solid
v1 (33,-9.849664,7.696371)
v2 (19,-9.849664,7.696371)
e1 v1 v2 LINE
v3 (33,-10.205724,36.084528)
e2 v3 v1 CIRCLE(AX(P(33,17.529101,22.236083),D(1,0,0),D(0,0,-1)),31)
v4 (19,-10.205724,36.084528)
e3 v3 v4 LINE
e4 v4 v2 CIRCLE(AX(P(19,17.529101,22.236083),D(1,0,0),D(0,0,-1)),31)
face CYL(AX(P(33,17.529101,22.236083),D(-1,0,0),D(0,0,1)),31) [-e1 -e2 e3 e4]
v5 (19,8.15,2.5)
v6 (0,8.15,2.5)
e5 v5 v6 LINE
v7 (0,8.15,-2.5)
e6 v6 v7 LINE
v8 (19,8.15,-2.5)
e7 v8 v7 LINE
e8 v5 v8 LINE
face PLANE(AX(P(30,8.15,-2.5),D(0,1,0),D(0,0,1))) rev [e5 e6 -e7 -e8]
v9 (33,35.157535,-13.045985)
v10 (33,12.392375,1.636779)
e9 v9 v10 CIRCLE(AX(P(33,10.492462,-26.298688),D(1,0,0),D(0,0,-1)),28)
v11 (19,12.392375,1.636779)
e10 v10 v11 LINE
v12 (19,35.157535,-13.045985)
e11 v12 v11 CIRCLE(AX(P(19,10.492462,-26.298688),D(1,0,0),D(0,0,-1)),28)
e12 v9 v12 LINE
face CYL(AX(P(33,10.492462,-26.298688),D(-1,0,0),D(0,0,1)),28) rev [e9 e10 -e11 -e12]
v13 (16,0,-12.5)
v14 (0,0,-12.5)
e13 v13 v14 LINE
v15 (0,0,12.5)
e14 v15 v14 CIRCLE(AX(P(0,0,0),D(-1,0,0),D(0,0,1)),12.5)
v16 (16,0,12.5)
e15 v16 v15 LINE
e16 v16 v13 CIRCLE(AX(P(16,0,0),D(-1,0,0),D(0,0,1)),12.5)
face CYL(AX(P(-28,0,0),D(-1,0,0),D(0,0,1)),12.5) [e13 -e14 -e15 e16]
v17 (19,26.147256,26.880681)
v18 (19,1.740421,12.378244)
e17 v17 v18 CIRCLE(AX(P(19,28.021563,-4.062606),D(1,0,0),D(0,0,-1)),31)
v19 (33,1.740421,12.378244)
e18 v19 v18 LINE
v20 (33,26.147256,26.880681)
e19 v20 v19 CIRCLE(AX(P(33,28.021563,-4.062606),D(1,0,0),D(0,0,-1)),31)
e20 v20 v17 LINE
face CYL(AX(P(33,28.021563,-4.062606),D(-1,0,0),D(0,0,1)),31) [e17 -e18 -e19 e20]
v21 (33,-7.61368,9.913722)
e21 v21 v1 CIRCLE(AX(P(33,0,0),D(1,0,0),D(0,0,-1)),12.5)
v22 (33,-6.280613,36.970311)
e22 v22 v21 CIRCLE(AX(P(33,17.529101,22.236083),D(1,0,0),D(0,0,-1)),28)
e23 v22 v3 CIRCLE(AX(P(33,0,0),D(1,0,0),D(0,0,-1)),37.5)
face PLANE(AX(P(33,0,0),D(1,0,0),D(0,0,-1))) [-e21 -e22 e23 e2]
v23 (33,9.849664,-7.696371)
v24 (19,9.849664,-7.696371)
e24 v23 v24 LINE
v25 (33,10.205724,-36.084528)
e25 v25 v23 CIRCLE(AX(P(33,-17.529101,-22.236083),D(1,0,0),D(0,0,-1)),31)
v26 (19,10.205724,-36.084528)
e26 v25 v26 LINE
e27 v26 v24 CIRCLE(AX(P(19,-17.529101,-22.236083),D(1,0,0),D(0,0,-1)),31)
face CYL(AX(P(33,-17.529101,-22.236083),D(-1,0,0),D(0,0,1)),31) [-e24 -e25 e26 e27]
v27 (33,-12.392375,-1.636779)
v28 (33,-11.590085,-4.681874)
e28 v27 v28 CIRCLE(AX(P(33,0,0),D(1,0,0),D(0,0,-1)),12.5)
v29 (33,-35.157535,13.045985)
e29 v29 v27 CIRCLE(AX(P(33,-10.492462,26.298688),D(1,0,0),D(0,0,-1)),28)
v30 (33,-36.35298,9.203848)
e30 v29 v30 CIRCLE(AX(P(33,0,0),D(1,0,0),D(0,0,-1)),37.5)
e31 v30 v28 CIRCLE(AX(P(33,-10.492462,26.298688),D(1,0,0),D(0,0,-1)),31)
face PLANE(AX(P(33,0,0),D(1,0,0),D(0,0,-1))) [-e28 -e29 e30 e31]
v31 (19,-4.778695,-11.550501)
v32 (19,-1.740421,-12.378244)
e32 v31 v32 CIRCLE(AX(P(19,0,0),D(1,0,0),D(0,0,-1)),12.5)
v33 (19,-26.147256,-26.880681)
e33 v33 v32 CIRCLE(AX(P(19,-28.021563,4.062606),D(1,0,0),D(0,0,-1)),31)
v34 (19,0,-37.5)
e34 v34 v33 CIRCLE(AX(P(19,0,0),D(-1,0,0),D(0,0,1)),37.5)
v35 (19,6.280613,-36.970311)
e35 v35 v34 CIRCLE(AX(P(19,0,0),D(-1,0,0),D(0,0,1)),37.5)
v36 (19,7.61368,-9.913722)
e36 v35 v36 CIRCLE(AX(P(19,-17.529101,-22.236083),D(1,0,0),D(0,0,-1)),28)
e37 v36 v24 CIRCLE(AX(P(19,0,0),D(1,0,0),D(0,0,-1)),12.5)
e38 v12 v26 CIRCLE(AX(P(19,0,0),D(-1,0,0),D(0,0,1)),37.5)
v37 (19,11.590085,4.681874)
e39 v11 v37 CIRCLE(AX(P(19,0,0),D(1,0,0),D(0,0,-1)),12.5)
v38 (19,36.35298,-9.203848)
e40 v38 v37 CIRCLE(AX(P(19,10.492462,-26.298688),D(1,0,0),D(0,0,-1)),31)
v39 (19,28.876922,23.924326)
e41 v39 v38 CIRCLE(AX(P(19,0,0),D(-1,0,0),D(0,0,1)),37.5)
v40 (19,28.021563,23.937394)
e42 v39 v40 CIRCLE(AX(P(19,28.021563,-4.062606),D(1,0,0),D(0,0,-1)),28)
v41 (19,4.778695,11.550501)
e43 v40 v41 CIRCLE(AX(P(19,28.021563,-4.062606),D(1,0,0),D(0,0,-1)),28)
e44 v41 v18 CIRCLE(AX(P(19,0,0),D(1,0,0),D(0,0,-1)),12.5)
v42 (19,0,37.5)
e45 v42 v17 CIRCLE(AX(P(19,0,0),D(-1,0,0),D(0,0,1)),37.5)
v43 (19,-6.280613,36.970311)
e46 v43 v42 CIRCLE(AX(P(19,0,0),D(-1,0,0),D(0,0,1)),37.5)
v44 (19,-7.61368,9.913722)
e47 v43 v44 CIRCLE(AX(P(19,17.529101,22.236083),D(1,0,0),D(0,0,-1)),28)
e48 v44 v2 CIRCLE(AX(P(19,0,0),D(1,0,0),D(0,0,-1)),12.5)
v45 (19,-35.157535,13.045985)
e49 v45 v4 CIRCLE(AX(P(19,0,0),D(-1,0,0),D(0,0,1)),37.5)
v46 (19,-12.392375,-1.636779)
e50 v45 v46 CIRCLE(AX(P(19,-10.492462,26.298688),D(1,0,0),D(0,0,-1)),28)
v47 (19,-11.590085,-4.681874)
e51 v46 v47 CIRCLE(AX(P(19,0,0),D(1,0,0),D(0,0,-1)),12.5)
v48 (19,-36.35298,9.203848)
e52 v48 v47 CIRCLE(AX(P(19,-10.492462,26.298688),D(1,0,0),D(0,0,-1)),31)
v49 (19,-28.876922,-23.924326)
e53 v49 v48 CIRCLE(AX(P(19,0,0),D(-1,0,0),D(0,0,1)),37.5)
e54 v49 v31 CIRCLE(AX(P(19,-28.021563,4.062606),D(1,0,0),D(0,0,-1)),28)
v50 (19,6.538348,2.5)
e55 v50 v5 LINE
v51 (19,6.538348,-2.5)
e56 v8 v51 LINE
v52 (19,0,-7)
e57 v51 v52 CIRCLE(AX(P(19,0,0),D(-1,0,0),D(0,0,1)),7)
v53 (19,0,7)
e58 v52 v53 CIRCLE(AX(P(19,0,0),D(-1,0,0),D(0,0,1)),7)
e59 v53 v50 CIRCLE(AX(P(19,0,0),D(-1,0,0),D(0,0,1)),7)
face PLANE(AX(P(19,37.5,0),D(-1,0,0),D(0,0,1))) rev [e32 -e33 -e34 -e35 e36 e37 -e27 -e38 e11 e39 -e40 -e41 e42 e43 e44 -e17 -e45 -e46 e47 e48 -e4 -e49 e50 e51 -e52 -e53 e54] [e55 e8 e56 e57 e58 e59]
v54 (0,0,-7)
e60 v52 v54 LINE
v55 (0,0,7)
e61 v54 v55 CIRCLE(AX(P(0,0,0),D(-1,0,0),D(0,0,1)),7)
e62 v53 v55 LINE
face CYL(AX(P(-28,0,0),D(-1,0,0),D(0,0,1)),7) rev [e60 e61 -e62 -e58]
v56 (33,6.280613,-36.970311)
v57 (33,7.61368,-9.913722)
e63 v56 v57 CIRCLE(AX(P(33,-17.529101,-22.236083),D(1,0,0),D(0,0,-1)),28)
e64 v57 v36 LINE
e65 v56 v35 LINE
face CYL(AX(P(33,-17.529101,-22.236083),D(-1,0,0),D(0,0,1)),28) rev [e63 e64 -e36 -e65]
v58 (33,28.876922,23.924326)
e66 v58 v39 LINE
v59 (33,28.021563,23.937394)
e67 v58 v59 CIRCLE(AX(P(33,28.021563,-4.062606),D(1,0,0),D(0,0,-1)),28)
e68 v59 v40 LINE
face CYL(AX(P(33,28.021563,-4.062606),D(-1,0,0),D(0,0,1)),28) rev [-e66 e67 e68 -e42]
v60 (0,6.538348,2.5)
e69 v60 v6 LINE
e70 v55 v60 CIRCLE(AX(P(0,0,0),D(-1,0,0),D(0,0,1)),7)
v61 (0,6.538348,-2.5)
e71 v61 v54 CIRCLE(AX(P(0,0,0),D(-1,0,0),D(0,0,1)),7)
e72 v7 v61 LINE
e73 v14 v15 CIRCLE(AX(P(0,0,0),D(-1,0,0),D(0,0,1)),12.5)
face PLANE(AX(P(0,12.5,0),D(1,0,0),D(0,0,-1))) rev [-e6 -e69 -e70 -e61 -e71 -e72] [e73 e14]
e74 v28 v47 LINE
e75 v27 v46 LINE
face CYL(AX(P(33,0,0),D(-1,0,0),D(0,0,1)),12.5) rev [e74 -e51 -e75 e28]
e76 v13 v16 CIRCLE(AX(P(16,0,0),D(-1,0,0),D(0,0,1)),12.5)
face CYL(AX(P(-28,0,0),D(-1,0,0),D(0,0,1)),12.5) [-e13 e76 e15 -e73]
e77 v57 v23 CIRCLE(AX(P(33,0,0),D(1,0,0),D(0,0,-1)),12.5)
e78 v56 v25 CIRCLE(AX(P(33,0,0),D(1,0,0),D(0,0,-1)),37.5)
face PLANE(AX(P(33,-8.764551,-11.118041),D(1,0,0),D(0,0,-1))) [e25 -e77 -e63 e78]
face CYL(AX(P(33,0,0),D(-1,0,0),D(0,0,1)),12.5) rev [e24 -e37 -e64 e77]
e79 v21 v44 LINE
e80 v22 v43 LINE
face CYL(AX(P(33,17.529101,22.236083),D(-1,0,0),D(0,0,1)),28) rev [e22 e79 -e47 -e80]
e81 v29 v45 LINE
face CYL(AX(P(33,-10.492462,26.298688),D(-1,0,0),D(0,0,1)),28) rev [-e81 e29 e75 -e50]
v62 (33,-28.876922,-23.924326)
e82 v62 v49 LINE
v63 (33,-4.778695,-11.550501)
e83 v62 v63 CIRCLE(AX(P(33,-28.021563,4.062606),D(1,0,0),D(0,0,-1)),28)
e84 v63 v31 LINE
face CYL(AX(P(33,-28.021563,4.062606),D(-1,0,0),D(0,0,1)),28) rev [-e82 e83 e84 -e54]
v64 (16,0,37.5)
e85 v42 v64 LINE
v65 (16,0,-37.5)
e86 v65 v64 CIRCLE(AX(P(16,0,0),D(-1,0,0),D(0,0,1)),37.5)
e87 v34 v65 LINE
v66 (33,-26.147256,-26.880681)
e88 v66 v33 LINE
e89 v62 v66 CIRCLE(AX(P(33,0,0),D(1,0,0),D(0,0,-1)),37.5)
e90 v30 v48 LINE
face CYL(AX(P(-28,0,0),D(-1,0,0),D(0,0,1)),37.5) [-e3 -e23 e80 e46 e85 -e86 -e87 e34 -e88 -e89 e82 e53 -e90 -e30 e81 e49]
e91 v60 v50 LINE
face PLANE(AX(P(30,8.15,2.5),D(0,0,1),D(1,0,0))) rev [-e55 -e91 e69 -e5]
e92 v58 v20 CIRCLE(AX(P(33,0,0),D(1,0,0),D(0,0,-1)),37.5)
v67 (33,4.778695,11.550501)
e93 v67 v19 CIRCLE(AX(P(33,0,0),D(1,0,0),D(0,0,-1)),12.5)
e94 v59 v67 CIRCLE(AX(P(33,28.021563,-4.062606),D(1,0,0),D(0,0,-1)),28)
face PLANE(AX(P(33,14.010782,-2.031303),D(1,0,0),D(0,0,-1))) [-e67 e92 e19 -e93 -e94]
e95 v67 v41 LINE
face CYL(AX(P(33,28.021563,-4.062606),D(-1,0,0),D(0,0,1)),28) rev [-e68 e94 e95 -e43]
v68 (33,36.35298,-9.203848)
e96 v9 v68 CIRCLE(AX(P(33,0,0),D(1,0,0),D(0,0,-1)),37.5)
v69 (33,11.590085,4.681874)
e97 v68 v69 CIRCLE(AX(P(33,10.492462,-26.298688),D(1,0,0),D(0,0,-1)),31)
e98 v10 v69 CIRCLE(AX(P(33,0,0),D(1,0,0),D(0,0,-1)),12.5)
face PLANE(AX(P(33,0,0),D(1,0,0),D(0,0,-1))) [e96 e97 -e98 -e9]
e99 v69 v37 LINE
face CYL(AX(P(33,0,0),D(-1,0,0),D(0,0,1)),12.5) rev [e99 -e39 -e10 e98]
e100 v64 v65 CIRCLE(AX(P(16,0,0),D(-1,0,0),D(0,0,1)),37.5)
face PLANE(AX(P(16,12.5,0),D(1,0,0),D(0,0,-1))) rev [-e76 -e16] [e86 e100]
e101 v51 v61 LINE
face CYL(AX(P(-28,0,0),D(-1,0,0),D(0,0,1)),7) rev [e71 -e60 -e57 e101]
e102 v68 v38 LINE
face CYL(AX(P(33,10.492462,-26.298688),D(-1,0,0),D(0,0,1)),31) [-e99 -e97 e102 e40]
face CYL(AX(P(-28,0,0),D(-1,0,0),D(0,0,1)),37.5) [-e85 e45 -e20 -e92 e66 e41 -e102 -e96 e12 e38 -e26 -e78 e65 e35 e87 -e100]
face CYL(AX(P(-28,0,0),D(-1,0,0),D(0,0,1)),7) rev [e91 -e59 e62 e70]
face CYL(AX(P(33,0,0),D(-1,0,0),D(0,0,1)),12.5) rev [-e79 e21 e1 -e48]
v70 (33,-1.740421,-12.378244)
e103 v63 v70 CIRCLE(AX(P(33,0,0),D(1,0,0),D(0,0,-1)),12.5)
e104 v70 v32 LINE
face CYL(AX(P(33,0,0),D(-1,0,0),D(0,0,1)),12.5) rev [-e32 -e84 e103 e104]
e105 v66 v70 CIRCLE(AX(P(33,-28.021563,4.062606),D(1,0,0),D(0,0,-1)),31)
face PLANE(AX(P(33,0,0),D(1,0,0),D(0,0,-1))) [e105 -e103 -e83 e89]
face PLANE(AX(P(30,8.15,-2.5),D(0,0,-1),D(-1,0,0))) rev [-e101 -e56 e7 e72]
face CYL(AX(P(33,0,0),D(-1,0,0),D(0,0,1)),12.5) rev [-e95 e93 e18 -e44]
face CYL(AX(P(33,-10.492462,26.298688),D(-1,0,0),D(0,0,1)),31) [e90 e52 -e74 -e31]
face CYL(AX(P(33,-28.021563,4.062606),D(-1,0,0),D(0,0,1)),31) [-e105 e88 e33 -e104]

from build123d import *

# Parameters (mm, degrees)
SHAFT_BORE_PROFILE_W = 5
SHAFT_BORE_PROFILE_H = 2.3
SHAFT_BORE_DEPTH     = 30
VANES_6X_DEPTH       = 14


with BuildPart() as part:
    # Hub Disc Profile → Hub and Back Disc (revolve)
    with BuildSketch(Plane.XY, mode=Mode.PRIVATE) as hub_and_back_disc_sk:
        Polygon((0, 12.5), (0, 7), (19, 7), (19, 37.5), (16, 37.5), (16, 12.5), align=None)
    revolve(hub_and_back_disc_sk.sketch.rotate(Axis((-28, 0, 0), (1, 0, 0)), 90), axis=Axis((-28, 0, 0), (1, 0, 0)))

    # Shaft Bore Profile → Shaft Bore (cut)
    with BuildSketch(Plane.ZY):
        with Locations((0, 7)):
            Rectangle(SHAFT_BORE_PROFILE_W, SHAFT_BORE_PROFILE_H)
    extrude(amount=-SHAFT_BORE_DEPTH, mode=Mode.SUBTRACT)

    # Vane Profiles 6x → Vanes 6x (add)
    with BuildSketch(Plane(origin=(19, 0, 0), x_dir=(0, 0, -1), z_dir=(1, 0, 0))):
        with BuildLine():
            ThreePointArc((-36.970311015, -6.2806133), (-36.580104109, -8.255058047), (-36.084528464, -10.205724156))
            ThreePointArc((-36.084528464, -10.205724156), (-21.847293577, -13.468460533), (-7.696370779, -9.849663793))
            ThreePointArc((-7.696370779, -9.849663793), (-8.875739318, -8.801775478), (-9.913722012, -7.613679523))
            ThreePointArc((-9.913722012, -7.613679523), (-23.613958858, -10.436975539), (-36.970311015, -6.2806133))
        make_face()
        with BuildLine():
            ThreePointArc((-13.045984839, -35.157535175), (-11.140962076, -35.806828455), (-9.203847848, -36.352980411))
            ThreePointArc((-9.203847848, -36.352980411), (0.740382183, -25.654541508), (4.681873674, -11.590084508))
            ThreePointArc((4.681873674, -11.590084508), (3.184691504, -12.087503465), (1.636778877, -12.39237487))
            ThreePointArc((1.636778877, -12.39237487), (-2.768293473, -25.668776024), (-13.045984839, -35.157535175))
        make_face()
        with BuildLine():
            ThreePointArc((23.924326177, -28.876921875), (25.439142033, -27.551770408), (26.880680615, -26.147256255))
            ThreePointArc((26.880680615, -26.147256255), (22.58767576, -12.186080975), (12.378244453, -1.740420715))
            ThreePointArc((12.378244453, -1.740420715), (12.060430821, -3.285727987), (11.550500889, -4.778695347))
            ThreePointArc((11.550500889, -4.778695347), (20.845665384, -15.231800485), (23.924326177, -28.876921875))
        make_face()
        with BuildLine():
            ThreePointArc((-1.636778877, 12.39237487), (2.768293473, 25.668776024), (13.045984839, 35.157535175))
            ThreePointArc((13.045984839, 35.157535175), (11.140962076, 35.806828455), (9.203847848, 36.352980411))
            ThreePointArc((9.203847848, 36.352980411), (-0.740382183, 25.654541508), (-4.681873674, 11.590084508))
            ThreePointArc((-4.681873674, 11.590084508), (-3.184691504, 12.087503465), (-1.636778877, 12.39237487))
        make_face()
        with BuildLine():
            ThreePointArc((-23.924326177, 28.876921875), (-20.845665384, 15.231800485), (-11.550500889, 4.778695347))
            ThreePointArc((-11.550500889, 4.778695347), (-12.060430821, 3.285727987), (-12.378244453, 1.740420715))
            ThreePointArc((-12.378244453, 1.740420715), (-22.58767576, 12.186080975), (-26.880680615, 26.147256255))
            ThreePointArc((-26.880680615, 26.147256255), (-25.439142033, 27.551770408), (-23.924326177, 28.876921875))
        make_face()
        with BuildLine():
            ThreePointArc((36.084528464, 10.205724156), (21.847293577, 13.468460533), (7.696370779, 9.849663793))
            ThreePointArc((7.696370779, 9.849663793), (8.875739318, 8.801775478), (9.913722012, 7.613679523))
            ThreePointArc((9.913722012, 7.613679523), (23.613958858, 10.436975539), (36.970311015, 6.2806133))
            ThreePointArc((36.970311015, 6.2806133), (36.580104109, 8.255058047), (36.084528464, 10.205724156))
        make_face()
    extrude(amount=VANES_6X_DEPTH)


solid = part.part
